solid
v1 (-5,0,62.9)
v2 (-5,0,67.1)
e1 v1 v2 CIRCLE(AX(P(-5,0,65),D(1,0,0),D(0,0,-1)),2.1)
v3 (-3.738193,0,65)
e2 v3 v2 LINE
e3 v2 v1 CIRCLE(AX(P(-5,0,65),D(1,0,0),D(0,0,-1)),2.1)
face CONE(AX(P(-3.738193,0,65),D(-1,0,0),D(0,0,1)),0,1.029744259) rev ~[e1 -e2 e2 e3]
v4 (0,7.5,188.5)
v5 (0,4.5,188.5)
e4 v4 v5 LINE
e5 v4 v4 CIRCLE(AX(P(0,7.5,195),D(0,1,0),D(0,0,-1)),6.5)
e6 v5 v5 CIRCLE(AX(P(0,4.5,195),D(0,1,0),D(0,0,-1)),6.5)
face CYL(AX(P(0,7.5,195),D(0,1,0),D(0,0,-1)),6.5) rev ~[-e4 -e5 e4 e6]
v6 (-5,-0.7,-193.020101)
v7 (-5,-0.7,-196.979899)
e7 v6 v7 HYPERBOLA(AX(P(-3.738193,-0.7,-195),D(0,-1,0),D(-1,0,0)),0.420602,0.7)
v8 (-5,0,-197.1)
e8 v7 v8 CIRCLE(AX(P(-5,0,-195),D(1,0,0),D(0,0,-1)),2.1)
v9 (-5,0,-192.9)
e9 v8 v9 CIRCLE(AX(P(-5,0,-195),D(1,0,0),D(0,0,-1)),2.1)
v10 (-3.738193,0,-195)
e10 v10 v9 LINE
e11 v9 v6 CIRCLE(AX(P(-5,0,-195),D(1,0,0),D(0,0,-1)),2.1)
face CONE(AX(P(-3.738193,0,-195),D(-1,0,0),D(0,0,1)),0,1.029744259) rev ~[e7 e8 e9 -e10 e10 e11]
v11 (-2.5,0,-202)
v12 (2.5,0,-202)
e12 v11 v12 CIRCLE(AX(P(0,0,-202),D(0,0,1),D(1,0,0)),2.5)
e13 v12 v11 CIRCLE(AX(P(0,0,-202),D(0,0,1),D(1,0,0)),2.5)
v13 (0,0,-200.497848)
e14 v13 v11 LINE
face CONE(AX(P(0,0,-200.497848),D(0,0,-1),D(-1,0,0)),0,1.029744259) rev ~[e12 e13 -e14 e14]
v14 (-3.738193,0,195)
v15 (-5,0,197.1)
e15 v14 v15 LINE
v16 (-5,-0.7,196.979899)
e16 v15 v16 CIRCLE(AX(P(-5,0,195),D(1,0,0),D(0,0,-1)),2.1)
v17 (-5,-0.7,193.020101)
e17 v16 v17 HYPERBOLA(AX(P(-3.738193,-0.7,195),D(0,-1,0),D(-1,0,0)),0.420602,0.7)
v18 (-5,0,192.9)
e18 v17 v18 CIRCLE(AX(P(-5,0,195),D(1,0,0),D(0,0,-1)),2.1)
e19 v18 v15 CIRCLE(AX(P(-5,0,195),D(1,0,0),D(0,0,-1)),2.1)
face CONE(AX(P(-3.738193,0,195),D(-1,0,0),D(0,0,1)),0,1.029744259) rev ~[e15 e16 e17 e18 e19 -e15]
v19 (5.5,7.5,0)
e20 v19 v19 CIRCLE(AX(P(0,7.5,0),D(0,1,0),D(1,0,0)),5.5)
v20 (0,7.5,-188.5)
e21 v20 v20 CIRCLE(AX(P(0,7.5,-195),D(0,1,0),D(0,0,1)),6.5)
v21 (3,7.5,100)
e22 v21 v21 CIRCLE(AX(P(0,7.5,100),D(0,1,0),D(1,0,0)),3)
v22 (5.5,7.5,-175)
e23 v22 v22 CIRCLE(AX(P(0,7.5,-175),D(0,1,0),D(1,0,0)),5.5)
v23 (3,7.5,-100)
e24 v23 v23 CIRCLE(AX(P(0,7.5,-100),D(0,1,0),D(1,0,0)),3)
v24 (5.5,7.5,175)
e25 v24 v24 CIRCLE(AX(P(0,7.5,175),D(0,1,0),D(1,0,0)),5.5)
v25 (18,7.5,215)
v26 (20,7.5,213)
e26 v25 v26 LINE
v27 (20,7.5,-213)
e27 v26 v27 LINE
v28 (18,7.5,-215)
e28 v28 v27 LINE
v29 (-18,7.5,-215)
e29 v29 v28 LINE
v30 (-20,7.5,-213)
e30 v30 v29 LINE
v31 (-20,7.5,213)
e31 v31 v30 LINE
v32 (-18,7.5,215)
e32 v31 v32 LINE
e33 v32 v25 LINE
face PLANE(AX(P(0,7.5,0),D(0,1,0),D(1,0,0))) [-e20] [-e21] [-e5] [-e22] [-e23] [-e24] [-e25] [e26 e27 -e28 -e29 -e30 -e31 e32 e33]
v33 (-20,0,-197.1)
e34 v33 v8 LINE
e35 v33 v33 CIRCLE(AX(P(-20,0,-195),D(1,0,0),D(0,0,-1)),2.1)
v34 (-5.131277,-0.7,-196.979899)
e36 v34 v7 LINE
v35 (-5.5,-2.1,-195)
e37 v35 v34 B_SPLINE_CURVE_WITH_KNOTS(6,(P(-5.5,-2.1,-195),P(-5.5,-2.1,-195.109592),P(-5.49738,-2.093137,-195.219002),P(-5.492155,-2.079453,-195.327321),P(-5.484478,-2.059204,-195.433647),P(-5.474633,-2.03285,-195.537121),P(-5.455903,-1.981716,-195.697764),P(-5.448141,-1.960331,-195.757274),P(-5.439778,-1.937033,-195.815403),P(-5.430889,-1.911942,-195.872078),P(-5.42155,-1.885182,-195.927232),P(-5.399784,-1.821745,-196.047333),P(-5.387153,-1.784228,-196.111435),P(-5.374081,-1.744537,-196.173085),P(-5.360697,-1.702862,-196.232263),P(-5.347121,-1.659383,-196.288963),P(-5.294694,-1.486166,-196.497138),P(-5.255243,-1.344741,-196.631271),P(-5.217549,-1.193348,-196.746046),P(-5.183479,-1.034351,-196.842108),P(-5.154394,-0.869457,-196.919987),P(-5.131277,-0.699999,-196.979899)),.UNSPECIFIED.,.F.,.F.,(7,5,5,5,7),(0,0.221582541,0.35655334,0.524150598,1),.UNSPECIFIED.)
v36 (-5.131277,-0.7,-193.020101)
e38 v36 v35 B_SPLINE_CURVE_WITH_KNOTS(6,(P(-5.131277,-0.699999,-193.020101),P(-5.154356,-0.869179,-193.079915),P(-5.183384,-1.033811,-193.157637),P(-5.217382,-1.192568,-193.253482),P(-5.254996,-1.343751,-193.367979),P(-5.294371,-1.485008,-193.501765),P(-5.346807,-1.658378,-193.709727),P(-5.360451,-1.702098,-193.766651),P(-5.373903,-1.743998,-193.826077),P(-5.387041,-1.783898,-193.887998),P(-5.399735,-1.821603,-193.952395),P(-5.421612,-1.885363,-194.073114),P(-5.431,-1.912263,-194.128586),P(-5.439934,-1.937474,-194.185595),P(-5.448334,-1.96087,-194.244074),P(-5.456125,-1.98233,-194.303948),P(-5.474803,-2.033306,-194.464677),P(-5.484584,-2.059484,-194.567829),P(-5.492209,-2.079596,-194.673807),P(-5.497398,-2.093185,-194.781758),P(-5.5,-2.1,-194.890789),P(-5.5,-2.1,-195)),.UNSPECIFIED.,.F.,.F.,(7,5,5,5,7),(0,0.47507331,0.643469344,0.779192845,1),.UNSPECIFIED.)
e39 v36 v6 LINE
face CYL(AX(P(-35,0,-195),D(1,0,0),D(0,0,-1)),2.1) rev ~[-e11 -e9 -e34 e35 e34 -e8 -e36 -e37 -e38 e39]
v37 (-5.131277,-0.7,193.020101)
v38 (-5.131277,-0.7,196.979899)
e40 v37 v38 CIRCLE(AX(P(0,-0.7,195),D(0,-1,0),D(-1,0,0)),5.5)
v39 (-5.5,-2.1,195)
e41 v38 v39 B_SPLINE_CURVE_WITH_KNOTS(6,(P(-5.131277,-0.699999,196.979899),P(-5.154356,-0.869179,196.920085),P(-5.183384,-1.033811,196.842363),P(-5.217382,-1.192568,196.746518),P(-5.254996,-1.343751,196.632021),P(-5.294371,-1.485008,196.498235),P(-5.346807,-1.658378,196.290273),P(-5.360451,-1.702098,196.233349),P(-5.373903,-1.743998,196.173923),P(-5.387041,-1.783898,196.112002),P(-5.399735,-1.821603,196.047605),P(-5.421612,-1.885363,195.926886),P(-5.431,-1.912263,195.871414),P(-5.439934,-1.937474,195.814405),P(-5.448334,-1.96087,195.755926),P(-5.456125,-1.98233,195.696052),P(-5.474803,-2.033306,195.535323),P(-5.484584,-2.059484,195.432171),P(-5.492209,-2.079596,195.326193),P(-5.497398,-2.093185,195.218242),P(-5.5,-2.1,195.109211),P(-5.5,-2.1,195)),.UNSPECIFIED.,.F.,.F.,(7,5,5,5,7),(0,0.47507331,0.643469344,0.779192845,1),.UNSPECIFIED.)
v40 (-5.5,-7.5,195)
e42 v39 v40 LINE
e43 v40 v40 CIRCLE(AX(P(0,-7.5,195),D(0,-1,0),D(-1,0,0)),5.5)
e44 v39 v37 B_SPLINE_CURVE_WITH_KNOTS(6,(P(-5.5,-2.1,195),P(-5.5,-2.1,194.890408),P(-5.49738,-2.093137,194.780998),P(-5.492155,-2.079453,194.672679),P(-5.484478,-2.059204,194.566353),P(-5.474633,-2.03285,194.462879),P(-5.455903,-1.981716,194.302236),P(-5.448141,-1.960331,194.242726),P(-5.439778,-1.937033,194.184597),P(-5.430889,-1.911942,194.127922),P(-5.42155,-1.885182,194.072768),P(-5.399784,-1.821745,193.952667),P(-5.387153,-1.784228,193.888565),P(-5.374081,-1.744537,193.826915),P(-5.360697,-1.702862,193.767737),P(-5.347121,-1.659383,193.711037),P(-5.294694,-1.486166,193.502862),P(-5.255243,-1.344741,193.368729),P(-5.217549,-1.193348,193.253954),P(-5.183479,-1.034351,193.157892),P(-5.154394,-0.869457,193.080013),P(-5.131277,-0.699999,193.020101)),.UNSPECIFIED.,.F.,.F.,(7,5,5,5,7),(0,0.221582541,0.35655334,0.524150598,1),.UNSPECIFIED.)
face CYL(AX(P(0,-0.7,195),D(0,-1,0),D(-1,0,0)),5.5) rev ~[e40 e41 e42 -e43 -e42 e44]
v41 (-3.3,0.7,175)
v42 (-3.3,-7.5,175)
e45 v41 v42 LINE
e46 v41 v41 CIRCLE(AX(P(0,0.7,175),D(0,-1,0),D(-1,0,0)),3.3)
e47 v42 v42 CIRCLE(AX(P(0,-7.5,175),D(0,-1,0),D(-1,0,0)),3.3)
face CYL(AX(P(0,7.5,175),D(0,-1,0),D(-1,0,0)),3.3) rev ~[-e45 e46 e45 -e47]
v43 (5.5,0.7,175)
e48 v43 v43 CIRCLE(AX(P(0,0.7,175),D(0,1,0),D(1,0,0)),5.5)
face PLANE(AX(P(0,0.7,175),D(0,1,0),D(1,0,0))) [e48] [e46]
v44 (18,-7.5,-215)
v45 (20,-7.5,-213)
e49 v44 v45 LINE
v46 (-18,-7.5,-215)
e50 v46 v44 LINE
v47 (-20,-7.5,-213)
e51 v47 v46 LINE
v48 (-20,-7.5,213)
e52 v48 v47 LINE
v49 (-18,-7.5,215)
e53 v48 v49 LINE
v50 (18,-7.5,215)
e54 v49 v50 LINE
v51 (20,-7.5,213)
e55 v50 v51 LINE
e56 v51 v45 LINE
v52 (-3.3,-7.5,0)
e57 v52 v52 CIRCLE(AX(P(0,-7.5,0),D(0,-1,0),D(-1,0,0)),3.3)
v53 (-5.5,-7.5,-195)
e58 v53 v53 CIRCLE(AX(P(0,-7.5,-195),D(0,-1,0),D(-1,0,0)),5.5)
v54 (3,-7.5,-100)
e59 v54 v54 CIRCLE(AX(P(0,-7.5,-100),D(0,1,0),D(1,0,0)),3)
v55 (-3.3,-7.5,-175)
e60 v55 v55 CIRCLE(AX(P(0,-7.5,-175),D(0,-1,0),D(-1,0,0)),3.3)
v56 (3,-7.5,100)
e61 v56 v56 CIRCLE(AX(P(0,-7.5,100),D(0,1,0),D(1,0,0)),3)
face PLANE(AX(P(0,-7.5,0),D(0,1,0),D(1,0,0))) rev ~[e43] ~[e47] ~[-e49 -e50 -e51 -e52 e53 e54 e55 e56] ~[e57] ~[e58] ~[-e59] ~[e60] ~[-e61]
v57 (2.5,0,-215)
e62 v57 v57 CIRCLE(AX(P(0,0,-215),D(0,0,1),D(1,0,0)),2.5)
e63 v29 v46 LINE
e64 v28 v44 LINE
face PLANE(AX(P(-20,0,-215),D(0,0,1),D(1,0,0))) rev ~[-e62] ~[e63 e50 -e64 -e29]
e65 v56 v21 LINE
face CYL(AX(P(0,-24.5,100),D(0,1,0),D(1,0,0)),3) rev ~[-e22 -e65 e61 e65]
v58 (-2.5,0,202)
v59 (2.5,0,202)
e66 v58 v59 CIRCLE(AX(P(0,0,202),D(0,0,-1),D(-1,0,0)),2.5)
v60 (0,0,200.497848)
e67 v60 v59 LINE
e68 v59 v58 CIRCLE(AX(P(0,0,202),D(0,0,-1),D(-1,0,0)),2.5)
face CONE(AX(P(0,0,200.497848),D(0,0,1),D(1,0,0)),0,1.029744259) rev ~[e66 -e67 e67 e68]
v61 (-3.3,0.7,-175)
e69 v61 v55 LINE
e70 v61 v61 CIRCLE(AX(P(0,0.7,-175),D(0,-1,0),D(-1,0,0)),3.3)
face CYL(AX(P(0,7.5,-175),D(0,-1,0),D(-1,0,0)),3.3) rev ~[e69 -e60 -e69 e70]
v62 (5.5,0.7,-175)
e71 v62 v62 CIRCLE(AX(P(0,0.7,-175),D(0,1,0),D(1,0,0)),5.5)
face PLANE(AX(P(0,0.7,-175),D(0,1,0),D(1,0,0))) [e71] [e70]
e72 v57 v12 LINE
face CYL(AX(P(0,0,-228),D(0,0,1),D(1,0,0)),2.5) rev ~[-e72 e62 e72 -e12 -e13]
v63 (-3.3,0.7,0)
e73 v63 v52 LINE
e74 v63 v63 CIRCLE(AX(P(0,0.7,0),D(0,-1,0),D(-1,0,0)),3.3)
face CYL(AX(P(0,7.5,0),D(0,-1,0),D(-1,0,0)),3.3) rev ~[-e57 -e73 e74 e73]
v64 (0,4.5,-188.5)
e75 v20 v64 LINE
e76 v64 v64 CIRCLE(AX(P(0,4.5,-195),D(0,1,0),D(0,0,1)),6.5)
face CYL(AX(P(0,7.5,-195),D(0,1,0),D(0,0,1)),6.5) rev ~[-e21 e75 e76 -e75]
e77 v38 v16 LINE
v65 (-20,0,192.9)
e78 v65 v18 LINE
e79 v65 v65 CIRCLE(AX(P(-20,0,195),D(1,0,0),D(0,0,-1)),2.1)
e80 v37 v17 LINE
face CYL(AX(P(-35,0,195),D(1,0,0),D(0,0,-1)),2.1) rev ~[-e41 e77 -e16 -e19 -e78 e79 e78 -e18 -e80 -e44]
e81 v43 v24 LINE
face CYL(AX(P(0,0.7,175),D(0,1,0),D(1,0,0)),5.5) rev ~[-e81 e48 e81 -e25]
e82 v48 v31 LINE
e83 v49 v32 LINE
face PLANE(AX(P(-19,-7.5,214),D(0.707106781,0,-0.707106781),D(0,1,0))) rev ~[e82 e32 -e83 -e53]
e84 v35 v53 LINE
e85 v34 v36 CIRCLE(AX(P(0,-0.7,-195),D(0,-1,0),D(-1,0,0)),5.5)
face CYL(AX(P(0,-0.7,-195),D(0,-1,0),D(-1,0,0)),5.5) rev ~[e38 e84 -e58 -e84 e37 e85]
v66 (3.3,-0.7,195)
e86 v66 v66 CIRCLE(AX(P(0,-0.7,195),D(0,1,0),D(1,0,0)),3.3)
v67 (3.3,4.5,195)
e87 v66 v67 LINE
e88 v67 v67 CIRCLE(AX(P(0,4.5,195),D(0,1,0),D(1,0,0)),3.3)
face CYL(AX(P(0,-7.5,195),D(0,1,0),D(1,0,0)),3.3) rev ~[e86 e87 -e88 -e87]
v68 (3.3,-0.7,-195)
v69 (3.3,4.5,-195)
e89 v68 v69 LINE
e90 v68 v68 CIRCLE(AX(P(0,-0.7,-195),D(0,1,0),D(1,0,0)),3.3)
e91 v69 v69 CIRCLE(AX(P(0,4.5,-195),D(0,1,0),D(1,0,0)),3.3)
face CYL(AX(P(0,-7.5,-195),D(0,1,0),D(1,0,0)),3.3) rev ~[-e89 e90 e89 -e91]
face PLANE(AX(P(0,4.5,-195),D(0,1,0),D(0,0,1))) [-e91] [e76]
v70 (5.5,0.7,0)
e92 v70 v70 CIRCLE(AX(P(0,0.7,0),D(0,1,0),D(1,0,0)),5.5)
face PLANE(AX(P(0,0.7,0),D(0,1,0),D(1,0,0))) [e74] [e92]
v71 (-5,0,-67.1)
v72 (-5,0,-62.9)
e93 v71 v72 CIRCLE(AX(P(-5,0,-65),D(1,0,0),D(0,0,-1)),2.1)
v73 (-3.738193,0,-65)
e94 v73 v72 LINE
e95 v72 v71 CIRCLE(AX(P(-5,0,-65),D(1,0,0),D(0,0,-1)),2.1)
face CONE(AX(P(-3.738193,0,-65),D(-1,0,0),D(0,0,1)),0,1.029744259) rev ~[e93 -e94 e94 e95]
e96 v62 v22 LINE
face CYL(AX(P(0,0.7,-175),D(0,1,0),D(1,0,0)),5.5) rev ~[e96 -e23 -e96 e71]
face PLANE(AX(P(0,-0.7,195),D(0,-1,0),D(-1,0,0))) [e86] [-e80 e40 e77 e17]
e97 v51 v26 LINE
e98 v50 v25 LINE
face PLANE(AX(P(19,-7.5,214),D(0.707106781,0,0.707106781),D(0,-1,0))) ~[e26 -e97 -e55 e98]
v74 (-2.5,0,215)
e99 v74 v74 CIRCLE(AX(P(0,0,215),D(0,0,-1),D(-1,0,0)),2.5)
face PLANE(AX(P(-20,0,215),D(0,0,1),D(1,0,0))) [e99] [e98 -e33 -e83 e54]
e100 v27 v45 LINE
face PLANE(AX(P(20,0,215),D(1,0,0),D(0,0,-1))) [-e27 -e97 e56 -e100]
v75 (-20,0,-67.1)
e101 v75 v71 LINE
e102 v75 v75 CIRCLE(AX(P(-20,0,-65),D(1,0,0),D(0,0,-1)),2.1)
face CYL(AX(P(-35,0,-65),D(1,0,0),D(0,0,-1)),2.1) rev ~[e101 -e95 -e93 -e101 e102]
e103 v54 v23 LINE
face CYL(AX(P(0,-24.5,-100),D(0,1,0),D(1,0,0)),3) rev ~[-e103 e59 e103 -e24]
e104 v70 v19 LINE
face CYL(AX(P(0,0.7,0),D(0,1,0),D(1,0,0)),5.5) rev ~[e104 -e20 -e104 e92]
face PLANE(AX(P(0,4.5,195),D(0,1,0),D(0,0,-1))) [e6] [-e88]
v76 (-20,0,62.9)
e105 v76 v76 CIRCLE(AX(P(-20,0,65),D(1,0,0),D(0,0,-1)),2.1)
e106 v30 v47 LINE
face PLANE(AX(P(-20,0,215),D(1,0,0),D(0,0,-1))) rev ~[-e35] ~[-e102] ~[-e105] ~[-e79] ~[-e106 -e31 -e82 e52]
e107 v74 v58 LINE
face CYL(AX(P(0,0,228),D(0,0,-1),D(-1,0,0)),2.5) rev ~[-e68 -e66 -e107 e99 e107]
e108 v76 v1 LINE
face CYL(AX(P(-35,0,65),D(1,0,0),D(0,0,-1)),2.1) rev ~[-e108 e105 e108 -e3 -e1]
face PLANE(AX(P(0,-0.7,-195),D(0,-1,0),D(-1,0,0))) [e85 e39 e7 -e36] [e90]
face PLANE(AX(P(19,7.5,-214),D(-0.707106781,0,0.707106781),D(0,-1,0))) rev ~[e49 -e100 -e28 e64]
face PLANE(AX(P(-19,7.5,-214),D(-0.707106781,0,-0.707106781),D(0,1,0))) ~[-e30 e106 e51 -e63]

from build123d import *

# Parameters (mm, degrees)
SKETCH1_W                                    = 40
SKETCH1_H                                    = 430
BOSS_EXTRUDE1_DEPTH                          = 7.5
SKETCH2_R                                    = 6.5
CUT_EXTRUDE1_DEPTH                           = 3
HEX_SOCKET_CAP_SCREW_HOLE_TYPE_1_D           = 6.6
HEX_SOCKET_CAP_SCREW_HOLE_TYPE_1_CBORE_D     = 11
HEX_SOCKET_CAP_SCREW_HOLE_TYPE_1_CBORE_DEPTH = 6.8
M5_TAPPED_HOLE1_D                            = 4.2
M5_TAPPED_HOLE1_DEPTH                        = 15
M5_TAPPED_HOLE1_TIP                          = 1.2618073
CHAMFER1_SIZE                                = 2
HEX_SOCKET_CAP_SCREW_HOLE_TYPE_2_D           = 6.6
HEX_SOCKET_CAP_SCREW_HOLE_TYPE_2_CBORE_D     = 11
HEX_SOCKET_CAP_SCREW_HOLE_TYPE_2_CBORE_DEPTH = 6.8
M6_TAPPED_HOLE1_D                            = 5
M6_TAPPED_HOLE1_DEPTH                        = 13
M6_TAPPED_HOLE1_TIP                          = 1.502151548
M6_TAPPED_HOLE2_D                            = 5
M6_TAPPED_HOLE2_DEPTH                        = 13
M6_TAPPED_HOLE2_TIP                          = 1.502151548
F_6_0_6_DIAMETER_HOLE1_D                     = 6
F_6_0_6_DIAMETER_HOLE1_DEPTH                 = 17
F_6_0_6_DIAMETER_HOLE1_TIP                   = 1.802581857


with BuildPart() as part:
    # Sketch1 → Boss-Extrude1 (new, symmetric)
    with BuildSketch(Plane(origin=(0, 0, 0), x_dir=(1, 0, 0), z_dir=(0, 1, 0))):
        Rectangle(SKETCH1_W, SKETCH1_H)
    extrude(amount=BOSS_EXTRUDE1_DEPTH, both=True)

    # Sketch2 → Cut-Extrude1 (cut)
    with BuildSketch(Plane(origin=(0, 7.5, 0), x_dir=(1, 0, 0), z_dir=(0, 1, 0))):
        with Locations(Location((0, 195, 0), (0, 0, 270))):
            Circle(SKETCH2_R)
        with Locations(Location((0, -195, 0), (0, 0, 90))):
            Circle(SKETCH2_R)
    extrude(amount=-CUT_EXTRUDE1_DEPTH, mode=Mode.SUBTRACT)

    # Hex socket cap screw hole type 1 (through all)
    with Locations(Plane(origin=(0, -7.5, 0), x_dir=(-1, 0, 0), z_dir=(0, -1, 0))):
        with Locations((0, -195), (0, 195)):
            CounterBoreHole(HEX_SOCKET_CAP_SCREW_HOLE_TYPE_1_D / 2, HEX_SOCKET_CAP_SCREW_HOLE_TYPE_1_CBORE_D / 2, HEX_SOCKET_CAP_SCREW_HOLE_TYPE_1_CBORE_DEPTH)

    # M5 Tapped Hole1
    with Locations(Plane.ZY.offset(20)):
        with Locations((-195, 0), (195, 0), (-65, 0), (65, 0)):
            Hole(M5_TAPPED_HOLE1_D / 2, depth=M5_TAPPED_HOLE1_DEPTH)
            with Locations((0, 0, -(M5_TAPPED_HOLE1_DEPTH + M5_TAPPED_HOLE1_TIP / 2))):  # 118° drill point
                Cone(0, M5_TAPPED_HOLE1_D / 2, M5_TAPPED_HOLE1_TIP, mode=Mode.SUBTRACT)

    # Chamfer1
    chamfer1_edges = [part.edges().sort_by_distance(p)[0] for p in [
        (-20, 0, -215),
        (20, 0, -215),
        (20, 0, 215),
        (-20, 0, 215),
    ]]
    chamfer(chamfer1_edges, length=CHAMFER1_SIZE)

    # Hex socket cap screw hole type 2 (through all)
    with Locations(Plane(origin=(0, 7.5, 0), x_dir=(1, 0, 0), z_dir=(0, 1, 0))):
        with Locations((0, 175), (0, -175), (0, 0)):
            CounterBoreHole(HEX_SOCKET_CAP_SCREW_HOLE_TYPE_2_D / 2, HEX_SOCKET_CAP_SCREW_HOLE_TYPE_2_CBORE_D / 2, HEX_SOCKET_CAP_SCREW_HOLE_TYPE_2_CBORE_DEPTH)

    # M6 Tapped Hole1
    with Locations(Plane.XY.offset(215)):
        with Locations((0, 0)):
            Hole(M6_TAPPED_HOLE1_D / 2, depth=M6_TAPPED_HOLE1_DEPTH)
            with Locations((0, 0, -(M6_TAPPED_HOLE1_DEPTH + M6_TAPPED_HOLE1_TIP / 2))):  # 118° drill point
                Cone(0, M6_TAPPED_HOLE1_D / 2, M6_TAPPED_HOLE1_TIP, mode=Mode.SUBTRACT)

    # M6 Tapped Hole2
    with Locations(Plane(origin=(0, 0, -215), x_dir=(-1, 0, 0), z_dir=(0, 0, -1))):
        with Locations((0, 0)):
            Hole(M6_TAPPED_HOLE2_D / 2, depth=M6_TAPPED_HOLE2_DEPTH)
            with Locations((0, 0, -(M6_TAPPED_HOLE2_DEPTH + M6_TAPPED_HOLE2_TIP / 2))):  # 118° drill point
                Cone(0, M6_TAPPED_HOLE2_D / 2, M6_TAPPED_HOLE2_TIP, mode=Mode.SUBTRACT)

    # Ø6.0 (6) Diameter Hole1
    with Locations(Plane(origin=(0, -7.5, 0), x_dir=(-1, 0, 0), z_dir=(0, -1, 0))):
        with Locations((0, 100), (0, -100)):
            Hole(F_6_0_6_DIAMETER_HOLE1_D / 2, depth=F_6_0_6_DIAMETER_HOLE1_DEPTH)
            with Locations((0, 0, -(F_6_0_6_DIAMETER_HOLE1_DEPTH + F_6_0_6_DIAMETER_HOLE1_TIP / 2))):  # 118° drill point
                Cone(0, F_6_0_6_DIAMETER_HOLE1_D / 2, F_6_0_6_DIAMETER_HOLE1_TIP, mode=Mode.SUBTRACT)


solid = part.part
